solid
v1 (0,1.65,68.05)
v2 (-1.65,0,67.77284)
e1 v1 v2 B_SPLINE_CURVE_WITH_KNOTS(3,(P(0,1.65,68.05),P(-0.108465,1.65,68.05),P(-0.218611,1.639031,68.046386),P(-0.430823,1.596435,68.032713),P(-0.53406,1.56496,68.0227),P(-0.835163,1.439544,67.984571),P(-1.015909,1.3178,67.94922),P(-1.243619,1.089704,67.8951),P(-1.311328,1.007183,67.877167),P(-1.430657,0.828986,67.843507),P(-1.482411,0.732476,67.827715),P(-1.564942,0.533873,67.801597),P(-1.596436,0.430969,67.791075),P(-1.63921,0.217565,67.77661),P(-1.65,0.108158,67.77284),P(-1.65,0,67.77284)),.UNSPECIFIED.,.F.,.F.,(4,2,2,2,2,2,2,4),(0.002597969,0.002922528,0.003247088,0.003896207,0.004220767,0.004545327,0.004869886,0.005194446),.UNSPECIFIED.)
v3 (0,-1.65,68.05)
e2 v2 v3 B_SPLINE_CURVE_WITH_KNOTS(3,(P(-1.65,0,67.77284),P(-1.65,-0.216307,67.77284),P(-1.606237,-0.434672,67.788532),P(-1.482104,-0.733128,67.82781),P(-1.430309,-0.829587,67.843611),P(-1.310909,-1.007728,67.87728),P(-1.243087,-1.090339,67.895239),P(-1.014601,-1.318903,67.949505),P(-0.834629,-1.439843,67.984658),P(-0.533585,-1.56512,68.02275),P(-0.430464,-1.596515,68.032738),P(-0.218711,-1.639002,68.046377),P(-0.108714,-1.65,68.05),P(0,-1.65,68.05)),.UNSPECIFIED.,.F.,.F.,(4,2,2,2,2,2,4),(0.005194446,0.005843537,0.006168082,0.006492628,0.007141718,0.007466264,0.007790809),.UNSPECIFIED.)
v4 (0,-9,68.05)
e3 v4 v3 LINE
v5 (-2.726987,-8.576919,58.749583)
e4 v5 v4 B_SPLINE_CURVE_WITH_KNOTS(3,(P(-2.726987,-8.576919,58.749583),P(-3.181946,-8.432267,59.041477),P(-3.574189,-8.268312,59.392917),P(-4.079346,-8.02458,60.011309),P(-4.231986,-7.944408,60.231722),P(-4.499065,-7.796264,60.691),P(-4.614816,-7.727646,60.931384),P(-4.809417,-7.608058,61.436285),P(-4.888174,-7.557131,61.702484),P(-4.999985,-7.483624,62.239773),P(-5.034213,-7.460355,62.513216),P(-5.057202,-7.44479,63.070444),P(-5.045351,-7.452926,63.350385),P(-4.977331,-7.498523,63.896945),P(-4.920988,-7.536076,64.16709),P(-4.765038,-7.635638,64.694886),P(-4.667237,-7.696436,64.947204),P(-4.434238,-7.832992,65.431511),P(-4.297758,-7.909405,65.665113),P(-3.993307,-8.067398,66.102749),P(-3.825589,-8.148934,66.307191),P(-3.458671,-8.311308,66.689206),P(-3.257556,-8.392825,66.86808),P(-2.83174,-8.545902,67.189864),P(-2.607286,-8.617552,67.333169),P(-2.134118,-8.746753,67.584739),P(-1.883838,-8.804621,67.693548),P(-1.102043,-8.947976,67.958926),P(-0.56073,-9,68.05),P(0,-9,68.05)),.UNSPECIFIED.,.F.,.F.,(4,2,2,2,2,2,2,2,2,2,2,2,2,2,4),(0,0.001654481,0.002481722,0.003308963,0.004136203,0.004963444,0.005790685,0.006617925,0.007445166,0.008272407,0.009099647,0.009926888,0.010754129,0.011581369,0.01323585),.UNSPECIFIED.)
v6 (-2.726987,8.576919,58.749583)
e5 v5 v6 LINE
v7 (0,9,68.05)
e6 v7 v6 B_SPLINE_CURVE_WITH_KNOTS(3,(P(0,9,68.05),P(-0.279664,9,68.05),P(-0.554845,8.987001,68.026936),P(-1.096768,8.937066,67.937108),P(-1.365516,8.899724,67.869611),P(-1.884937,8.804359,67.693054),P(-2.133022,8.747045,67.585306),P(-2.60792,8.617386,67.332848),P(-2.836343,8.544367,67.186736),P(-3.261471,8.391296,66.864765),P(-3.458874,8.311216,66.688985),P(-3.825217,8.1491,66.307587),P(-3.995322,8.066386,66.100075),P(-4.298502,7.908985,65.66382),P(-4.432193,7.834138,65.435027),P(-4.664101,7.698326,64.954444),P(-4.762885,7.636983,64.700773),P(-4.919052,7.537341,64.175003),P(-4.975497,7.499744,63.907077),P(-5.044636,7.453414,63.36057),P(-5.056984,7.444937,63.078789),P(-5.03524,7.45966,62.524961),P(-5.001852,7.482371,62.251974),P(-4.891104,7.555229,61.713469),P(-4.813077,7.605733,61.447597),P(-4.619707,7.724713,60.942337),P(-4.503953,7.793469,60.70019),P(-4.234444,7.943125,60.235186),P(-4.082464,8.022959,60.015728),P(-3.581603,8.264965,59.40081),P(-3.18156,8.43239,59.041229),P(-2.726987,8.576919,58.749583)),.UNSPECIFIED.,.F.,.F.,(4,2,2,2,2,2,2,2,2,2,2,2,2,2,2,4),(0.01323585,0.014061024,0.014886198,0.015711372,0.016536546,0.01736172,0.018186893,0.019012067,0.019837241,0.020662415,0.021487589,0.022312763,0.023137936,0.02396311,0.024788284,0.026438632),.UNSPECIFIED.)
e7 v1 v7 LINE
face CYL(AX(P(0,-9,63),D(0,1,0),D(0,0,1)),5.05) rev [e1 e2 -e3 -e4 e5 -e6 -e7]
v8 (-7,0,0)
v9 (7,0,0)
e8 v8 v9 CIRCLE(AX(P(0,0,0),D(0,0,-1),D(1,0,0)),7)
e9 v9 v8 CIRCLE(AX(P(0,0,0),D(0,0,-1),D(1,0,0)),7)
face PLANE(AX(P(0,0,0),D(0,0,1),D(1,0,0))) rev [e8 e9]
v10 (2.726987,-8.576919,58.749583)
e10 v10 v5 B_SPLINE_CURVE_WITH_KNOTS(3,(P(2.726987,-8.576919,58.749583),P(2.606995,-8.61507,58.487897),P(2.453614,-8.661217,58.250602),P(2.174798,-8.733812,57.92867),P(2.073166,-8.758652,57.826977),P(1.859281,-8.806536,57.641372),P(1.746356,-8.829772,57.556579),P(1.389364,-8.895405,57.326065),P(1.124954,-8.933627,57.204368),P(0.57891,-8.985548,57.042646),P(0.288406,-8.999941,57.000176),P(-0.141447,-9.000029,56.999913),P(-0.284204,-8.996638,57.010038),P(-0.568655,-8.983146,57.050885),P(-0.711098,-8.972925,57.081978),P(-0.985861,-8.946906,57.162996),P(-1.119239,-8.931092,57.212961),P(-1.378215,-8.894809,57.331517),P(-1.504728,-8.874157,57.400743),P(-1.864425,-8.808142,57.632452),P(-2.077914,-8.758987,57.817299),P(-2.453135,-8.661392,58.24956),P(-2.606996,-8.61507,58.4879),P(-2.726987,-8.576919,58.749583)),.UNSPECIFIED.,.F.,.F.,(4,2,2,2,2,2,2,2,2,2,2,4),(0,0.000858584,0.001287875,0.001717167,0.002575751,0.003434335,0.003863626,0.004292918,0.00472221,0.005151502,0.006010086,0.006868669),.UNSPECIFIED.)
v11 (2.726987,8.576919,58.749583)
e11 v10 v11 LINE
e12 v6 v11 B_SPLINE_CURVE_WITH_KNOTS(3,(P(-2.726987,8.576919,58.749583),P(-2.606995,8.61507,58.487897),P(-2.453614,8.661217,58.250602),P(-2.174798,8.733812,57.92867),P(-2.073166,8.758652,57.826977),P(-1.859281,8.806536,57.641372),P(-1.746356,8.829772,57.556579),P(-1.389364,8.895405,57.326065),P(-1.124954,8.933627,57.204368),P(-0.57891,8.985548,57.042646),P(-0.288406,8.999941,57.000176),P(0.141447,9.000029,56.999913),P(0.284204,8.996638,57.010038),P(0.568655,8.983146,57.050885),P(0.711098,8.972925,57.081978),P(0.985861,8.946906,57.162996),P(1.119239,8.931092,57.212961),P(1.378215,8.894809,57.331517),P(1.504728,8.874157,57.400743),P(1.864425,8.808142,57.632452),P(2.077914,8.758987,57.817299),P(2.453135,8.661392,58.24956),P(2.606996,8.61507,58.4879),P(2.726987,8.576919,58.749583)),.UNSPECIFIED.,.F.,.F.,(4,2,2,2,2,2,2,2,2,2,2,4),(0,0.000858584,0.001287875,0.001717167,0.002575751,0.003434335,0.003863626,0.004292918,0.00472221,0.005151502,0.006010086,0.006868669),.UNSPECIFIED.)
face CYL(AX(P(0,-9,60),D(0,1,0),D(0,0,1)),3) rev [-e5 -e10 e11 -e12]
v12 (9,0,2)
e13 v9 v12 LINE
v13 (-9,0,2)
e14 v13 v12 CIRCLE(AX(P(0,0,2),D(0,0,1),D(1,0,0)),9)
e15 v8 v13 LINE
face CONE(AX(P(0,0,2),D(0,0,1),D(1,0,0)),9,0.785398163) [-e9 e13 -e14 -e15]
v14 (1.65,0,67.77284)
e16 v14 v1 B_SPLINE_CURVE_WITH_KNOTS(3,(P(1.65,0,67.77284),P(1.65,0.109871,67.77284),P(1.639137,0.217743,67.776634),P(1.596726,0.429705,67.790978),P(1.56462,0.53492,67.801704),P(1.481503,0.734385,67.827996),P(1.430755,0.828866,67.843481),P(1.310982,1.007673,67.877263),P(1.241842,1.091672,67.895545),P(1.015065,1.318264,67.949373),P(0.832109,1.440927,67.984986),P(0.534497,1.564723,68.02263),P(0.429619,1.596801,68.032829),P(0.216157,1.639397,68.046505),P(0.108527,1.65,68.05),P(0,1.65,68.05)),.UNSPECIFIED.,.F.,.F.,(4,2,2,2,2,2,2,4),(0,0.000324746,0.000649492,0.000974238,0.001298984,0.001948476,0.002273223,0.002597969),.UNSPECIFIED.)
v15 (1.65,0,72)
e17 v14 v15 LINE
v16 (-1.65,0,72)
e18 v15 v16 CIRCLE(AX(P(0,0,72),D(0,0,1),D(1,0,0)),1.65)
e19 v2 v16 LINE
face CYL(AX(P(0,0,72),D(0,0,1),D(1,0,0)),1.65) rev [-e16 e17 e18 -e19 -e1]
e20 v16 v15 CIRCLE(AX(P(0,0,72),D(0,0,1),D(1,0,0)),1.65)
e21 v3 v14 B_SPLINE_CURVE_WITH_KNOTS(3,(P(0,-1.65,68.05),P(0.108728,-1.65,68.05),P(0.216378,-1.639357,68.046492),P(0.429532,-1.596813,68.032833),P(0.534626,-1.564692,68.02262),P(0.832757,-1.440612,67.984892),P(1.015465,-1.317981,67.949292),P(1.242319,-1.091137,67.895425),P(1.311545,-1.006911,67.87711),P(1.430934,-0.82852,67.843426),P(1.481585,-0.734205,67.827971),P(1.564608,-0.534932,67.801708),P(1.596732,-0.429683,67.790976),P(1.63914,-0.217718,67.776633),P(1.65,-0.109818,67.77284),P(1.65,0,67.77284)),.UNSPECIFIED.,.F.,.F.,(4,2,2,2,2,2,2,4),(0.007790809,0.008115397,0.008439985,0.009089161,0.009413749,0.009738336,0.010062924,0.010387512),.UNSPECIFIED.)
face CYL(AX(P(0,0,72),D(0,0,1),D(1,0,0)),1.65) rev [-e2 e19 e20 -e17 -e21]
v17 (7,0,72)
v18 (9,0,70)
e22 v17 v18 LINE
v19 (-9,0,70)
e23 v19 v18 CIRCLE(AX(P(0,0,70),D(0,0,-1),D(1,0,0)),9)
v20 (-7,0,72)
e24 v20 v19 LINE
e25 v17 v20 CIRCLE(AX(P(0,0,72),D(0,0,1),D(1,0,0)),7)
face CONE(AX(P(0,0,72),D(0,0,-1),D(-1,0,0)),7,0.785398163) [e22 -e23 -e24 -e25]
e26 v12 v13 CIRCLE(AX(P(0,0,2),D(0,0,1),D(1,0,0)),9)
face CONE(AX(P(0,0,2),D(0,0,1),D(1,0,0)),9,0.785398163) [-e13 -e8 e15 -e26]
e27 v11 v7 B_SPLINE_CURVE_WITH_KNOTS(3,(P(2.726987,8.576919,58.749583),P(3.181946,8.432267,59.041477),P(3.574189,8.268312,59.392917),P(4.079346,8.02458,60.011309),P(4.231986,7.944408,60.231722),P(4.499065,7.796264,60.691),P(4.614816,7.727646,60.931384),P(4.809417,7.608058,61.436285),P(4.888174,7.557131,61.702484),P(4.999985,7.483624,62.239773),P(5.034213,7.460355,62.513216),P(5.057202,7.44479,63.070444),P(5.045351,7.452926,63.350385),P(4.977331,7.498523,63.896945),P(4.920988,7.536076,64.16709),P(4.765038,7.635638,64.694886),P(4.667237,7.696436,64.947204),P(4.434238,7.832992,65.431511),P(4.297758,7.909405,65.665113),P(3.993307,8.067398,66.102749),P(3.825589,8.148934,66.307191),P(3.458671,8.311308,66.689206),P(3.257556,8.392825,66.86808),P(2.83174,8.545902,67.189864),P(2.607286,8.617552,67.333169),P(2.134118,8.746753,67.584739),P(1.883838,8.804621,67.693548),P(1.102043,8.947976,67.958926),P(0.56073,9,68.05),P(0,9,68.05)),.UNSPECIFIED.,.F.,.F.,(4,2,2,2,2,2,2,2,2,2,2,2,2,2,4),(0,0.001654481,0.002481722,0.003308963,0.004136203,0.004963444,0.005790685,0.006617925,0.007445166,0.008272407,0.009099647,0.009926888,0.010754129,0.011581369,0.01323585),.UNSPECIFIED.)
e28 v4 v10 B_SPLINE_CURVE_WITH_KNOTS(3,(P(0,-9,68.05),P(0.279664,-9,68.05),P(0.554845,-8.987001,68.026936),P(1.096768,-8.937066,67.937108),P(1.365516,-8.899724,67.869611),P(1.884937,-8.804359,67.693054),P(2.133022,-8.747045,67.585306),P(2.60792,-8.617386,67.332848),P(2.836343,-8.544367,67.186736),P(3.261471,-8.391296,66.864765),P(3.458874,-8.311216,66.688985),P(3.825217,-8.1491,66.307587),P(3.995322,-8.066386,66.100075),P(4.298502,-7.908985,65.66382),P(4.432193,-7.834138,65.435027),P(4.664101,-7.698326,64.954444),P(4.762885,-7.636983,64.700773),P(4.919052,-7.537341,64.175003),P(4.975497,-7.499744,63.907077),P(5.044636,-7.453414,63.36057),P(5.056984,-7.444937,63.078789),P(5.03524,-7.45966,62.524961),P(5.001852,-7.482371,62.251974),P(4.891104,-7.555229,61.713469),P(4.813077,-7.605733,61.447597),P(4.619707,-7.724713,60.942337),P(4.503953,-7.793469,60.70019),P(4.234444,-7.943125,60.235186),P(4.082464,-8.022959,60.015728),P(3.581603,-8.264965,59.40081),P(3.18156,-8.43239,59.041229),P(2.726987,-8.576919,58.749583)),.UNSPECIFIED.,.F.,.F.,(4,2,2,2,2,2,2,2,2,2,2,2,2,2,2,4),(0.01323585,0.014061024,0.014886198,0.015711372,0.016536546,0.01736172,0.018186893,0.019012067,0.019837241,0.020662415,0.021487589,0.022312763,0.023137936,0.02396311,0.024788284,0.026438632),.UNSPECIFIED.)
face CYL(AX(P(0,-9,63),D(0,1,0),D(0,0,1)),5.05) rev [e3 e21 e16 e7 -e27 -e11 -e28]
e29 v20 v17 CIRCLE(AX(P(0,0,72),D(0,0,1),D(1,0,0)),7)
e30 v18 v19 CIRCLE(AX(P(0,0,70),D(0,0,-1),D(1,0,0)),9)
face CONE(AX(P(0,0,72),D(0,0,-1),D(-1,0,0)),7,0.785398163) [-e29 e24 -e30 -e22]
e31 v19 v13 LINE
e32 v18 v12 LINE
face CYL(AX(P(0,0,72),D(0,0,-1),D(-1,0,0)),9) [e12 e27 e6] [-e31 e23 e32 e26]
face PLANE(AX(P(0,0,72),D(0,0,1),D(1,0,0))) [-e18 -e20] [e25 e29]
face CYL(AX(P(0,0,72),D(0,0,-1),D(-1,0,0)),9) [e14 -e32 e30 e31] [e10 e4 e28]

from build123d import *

# Parameters (mm, degrees)
SKETCH1_R               = 9
BOSS_EXTRUDE1_DEPTH     = 72
CUT_EXTRUDE1_DEPTH      = 74.116345642
CUT_EXTRUDE1_DEPTH_BACK = 74.116345642
M4_TAPPED_HOLE1_REACH   = 75.116
M4_TAPPED_HOLE1_BORE_R  = 1.65
CHAMFER1_SIZE           = 2


with BuildPart() as part:
    # Sketch1 → Boss-Extrude1 (new body)
    with BuildSketch(Plane.XY):
        Circle(SKETCH1_R)
    extrude(amount=BOSS_EXTRUDE1_DEPTH)

    # Sketch2 → Cut-Extrude1 (cut, two sides: drawn at the far end of the back side and taken through both)
    with BuildSketch(Plane(origin=(0, 0, 0), x_dir=(1, 0, 0), z_dir=(0, 1, 0)).offset(-CUT_EXTRUDE1_DEPTH_BACK)):
        with BuildLine():
            ThreePointArc((-2.726987011, -58.749583333), (0, -68.05), (2.726987011, -58.749583333))
            ThreePointArc((2.726987011, -58.749583333), (0, -57), (-2.726987011, -58.749583333))
        make_face()
    extrude(amount=CUT_EXTRUDE1_DEPTH + CUT_EXTRUDE1_DEPTH_BACK, mode=Mode.SUBTRACT)

    # M4 Tapped Hole1 bore → M4 Tapped Hole1 (cut, up to next)
    with BuildSketch(Plane.XY.offset(72), mode=Mode.PRIVATE) as m4_tapped_hole1_sk1:
        Circle(M4_TAPPED_HOLE1_BORE_R)
    m4_tapped_hole1_tool1 = extrude(m4_tapped_hole1_sk1.sketch, amount=-M4_TAPPED_HOLE1_REACH, mode=Mode.PRIVATE) & part.part
    add(m4_tapped_hole1_tool1.solids().sort_by_distance((0, 0, 72))[0], mode=Mode.SUBTRACT)

    # Chamfer1
    chamfer1_edges = [part.edges().sort_by_distance(p)[0] for p in [
        (-9, 0, 0),
        (-9, 0, 72),
    ]]
    chamfer(chamfer1_edges, length=CHAMFER1_SIZE)


solid = part.part
